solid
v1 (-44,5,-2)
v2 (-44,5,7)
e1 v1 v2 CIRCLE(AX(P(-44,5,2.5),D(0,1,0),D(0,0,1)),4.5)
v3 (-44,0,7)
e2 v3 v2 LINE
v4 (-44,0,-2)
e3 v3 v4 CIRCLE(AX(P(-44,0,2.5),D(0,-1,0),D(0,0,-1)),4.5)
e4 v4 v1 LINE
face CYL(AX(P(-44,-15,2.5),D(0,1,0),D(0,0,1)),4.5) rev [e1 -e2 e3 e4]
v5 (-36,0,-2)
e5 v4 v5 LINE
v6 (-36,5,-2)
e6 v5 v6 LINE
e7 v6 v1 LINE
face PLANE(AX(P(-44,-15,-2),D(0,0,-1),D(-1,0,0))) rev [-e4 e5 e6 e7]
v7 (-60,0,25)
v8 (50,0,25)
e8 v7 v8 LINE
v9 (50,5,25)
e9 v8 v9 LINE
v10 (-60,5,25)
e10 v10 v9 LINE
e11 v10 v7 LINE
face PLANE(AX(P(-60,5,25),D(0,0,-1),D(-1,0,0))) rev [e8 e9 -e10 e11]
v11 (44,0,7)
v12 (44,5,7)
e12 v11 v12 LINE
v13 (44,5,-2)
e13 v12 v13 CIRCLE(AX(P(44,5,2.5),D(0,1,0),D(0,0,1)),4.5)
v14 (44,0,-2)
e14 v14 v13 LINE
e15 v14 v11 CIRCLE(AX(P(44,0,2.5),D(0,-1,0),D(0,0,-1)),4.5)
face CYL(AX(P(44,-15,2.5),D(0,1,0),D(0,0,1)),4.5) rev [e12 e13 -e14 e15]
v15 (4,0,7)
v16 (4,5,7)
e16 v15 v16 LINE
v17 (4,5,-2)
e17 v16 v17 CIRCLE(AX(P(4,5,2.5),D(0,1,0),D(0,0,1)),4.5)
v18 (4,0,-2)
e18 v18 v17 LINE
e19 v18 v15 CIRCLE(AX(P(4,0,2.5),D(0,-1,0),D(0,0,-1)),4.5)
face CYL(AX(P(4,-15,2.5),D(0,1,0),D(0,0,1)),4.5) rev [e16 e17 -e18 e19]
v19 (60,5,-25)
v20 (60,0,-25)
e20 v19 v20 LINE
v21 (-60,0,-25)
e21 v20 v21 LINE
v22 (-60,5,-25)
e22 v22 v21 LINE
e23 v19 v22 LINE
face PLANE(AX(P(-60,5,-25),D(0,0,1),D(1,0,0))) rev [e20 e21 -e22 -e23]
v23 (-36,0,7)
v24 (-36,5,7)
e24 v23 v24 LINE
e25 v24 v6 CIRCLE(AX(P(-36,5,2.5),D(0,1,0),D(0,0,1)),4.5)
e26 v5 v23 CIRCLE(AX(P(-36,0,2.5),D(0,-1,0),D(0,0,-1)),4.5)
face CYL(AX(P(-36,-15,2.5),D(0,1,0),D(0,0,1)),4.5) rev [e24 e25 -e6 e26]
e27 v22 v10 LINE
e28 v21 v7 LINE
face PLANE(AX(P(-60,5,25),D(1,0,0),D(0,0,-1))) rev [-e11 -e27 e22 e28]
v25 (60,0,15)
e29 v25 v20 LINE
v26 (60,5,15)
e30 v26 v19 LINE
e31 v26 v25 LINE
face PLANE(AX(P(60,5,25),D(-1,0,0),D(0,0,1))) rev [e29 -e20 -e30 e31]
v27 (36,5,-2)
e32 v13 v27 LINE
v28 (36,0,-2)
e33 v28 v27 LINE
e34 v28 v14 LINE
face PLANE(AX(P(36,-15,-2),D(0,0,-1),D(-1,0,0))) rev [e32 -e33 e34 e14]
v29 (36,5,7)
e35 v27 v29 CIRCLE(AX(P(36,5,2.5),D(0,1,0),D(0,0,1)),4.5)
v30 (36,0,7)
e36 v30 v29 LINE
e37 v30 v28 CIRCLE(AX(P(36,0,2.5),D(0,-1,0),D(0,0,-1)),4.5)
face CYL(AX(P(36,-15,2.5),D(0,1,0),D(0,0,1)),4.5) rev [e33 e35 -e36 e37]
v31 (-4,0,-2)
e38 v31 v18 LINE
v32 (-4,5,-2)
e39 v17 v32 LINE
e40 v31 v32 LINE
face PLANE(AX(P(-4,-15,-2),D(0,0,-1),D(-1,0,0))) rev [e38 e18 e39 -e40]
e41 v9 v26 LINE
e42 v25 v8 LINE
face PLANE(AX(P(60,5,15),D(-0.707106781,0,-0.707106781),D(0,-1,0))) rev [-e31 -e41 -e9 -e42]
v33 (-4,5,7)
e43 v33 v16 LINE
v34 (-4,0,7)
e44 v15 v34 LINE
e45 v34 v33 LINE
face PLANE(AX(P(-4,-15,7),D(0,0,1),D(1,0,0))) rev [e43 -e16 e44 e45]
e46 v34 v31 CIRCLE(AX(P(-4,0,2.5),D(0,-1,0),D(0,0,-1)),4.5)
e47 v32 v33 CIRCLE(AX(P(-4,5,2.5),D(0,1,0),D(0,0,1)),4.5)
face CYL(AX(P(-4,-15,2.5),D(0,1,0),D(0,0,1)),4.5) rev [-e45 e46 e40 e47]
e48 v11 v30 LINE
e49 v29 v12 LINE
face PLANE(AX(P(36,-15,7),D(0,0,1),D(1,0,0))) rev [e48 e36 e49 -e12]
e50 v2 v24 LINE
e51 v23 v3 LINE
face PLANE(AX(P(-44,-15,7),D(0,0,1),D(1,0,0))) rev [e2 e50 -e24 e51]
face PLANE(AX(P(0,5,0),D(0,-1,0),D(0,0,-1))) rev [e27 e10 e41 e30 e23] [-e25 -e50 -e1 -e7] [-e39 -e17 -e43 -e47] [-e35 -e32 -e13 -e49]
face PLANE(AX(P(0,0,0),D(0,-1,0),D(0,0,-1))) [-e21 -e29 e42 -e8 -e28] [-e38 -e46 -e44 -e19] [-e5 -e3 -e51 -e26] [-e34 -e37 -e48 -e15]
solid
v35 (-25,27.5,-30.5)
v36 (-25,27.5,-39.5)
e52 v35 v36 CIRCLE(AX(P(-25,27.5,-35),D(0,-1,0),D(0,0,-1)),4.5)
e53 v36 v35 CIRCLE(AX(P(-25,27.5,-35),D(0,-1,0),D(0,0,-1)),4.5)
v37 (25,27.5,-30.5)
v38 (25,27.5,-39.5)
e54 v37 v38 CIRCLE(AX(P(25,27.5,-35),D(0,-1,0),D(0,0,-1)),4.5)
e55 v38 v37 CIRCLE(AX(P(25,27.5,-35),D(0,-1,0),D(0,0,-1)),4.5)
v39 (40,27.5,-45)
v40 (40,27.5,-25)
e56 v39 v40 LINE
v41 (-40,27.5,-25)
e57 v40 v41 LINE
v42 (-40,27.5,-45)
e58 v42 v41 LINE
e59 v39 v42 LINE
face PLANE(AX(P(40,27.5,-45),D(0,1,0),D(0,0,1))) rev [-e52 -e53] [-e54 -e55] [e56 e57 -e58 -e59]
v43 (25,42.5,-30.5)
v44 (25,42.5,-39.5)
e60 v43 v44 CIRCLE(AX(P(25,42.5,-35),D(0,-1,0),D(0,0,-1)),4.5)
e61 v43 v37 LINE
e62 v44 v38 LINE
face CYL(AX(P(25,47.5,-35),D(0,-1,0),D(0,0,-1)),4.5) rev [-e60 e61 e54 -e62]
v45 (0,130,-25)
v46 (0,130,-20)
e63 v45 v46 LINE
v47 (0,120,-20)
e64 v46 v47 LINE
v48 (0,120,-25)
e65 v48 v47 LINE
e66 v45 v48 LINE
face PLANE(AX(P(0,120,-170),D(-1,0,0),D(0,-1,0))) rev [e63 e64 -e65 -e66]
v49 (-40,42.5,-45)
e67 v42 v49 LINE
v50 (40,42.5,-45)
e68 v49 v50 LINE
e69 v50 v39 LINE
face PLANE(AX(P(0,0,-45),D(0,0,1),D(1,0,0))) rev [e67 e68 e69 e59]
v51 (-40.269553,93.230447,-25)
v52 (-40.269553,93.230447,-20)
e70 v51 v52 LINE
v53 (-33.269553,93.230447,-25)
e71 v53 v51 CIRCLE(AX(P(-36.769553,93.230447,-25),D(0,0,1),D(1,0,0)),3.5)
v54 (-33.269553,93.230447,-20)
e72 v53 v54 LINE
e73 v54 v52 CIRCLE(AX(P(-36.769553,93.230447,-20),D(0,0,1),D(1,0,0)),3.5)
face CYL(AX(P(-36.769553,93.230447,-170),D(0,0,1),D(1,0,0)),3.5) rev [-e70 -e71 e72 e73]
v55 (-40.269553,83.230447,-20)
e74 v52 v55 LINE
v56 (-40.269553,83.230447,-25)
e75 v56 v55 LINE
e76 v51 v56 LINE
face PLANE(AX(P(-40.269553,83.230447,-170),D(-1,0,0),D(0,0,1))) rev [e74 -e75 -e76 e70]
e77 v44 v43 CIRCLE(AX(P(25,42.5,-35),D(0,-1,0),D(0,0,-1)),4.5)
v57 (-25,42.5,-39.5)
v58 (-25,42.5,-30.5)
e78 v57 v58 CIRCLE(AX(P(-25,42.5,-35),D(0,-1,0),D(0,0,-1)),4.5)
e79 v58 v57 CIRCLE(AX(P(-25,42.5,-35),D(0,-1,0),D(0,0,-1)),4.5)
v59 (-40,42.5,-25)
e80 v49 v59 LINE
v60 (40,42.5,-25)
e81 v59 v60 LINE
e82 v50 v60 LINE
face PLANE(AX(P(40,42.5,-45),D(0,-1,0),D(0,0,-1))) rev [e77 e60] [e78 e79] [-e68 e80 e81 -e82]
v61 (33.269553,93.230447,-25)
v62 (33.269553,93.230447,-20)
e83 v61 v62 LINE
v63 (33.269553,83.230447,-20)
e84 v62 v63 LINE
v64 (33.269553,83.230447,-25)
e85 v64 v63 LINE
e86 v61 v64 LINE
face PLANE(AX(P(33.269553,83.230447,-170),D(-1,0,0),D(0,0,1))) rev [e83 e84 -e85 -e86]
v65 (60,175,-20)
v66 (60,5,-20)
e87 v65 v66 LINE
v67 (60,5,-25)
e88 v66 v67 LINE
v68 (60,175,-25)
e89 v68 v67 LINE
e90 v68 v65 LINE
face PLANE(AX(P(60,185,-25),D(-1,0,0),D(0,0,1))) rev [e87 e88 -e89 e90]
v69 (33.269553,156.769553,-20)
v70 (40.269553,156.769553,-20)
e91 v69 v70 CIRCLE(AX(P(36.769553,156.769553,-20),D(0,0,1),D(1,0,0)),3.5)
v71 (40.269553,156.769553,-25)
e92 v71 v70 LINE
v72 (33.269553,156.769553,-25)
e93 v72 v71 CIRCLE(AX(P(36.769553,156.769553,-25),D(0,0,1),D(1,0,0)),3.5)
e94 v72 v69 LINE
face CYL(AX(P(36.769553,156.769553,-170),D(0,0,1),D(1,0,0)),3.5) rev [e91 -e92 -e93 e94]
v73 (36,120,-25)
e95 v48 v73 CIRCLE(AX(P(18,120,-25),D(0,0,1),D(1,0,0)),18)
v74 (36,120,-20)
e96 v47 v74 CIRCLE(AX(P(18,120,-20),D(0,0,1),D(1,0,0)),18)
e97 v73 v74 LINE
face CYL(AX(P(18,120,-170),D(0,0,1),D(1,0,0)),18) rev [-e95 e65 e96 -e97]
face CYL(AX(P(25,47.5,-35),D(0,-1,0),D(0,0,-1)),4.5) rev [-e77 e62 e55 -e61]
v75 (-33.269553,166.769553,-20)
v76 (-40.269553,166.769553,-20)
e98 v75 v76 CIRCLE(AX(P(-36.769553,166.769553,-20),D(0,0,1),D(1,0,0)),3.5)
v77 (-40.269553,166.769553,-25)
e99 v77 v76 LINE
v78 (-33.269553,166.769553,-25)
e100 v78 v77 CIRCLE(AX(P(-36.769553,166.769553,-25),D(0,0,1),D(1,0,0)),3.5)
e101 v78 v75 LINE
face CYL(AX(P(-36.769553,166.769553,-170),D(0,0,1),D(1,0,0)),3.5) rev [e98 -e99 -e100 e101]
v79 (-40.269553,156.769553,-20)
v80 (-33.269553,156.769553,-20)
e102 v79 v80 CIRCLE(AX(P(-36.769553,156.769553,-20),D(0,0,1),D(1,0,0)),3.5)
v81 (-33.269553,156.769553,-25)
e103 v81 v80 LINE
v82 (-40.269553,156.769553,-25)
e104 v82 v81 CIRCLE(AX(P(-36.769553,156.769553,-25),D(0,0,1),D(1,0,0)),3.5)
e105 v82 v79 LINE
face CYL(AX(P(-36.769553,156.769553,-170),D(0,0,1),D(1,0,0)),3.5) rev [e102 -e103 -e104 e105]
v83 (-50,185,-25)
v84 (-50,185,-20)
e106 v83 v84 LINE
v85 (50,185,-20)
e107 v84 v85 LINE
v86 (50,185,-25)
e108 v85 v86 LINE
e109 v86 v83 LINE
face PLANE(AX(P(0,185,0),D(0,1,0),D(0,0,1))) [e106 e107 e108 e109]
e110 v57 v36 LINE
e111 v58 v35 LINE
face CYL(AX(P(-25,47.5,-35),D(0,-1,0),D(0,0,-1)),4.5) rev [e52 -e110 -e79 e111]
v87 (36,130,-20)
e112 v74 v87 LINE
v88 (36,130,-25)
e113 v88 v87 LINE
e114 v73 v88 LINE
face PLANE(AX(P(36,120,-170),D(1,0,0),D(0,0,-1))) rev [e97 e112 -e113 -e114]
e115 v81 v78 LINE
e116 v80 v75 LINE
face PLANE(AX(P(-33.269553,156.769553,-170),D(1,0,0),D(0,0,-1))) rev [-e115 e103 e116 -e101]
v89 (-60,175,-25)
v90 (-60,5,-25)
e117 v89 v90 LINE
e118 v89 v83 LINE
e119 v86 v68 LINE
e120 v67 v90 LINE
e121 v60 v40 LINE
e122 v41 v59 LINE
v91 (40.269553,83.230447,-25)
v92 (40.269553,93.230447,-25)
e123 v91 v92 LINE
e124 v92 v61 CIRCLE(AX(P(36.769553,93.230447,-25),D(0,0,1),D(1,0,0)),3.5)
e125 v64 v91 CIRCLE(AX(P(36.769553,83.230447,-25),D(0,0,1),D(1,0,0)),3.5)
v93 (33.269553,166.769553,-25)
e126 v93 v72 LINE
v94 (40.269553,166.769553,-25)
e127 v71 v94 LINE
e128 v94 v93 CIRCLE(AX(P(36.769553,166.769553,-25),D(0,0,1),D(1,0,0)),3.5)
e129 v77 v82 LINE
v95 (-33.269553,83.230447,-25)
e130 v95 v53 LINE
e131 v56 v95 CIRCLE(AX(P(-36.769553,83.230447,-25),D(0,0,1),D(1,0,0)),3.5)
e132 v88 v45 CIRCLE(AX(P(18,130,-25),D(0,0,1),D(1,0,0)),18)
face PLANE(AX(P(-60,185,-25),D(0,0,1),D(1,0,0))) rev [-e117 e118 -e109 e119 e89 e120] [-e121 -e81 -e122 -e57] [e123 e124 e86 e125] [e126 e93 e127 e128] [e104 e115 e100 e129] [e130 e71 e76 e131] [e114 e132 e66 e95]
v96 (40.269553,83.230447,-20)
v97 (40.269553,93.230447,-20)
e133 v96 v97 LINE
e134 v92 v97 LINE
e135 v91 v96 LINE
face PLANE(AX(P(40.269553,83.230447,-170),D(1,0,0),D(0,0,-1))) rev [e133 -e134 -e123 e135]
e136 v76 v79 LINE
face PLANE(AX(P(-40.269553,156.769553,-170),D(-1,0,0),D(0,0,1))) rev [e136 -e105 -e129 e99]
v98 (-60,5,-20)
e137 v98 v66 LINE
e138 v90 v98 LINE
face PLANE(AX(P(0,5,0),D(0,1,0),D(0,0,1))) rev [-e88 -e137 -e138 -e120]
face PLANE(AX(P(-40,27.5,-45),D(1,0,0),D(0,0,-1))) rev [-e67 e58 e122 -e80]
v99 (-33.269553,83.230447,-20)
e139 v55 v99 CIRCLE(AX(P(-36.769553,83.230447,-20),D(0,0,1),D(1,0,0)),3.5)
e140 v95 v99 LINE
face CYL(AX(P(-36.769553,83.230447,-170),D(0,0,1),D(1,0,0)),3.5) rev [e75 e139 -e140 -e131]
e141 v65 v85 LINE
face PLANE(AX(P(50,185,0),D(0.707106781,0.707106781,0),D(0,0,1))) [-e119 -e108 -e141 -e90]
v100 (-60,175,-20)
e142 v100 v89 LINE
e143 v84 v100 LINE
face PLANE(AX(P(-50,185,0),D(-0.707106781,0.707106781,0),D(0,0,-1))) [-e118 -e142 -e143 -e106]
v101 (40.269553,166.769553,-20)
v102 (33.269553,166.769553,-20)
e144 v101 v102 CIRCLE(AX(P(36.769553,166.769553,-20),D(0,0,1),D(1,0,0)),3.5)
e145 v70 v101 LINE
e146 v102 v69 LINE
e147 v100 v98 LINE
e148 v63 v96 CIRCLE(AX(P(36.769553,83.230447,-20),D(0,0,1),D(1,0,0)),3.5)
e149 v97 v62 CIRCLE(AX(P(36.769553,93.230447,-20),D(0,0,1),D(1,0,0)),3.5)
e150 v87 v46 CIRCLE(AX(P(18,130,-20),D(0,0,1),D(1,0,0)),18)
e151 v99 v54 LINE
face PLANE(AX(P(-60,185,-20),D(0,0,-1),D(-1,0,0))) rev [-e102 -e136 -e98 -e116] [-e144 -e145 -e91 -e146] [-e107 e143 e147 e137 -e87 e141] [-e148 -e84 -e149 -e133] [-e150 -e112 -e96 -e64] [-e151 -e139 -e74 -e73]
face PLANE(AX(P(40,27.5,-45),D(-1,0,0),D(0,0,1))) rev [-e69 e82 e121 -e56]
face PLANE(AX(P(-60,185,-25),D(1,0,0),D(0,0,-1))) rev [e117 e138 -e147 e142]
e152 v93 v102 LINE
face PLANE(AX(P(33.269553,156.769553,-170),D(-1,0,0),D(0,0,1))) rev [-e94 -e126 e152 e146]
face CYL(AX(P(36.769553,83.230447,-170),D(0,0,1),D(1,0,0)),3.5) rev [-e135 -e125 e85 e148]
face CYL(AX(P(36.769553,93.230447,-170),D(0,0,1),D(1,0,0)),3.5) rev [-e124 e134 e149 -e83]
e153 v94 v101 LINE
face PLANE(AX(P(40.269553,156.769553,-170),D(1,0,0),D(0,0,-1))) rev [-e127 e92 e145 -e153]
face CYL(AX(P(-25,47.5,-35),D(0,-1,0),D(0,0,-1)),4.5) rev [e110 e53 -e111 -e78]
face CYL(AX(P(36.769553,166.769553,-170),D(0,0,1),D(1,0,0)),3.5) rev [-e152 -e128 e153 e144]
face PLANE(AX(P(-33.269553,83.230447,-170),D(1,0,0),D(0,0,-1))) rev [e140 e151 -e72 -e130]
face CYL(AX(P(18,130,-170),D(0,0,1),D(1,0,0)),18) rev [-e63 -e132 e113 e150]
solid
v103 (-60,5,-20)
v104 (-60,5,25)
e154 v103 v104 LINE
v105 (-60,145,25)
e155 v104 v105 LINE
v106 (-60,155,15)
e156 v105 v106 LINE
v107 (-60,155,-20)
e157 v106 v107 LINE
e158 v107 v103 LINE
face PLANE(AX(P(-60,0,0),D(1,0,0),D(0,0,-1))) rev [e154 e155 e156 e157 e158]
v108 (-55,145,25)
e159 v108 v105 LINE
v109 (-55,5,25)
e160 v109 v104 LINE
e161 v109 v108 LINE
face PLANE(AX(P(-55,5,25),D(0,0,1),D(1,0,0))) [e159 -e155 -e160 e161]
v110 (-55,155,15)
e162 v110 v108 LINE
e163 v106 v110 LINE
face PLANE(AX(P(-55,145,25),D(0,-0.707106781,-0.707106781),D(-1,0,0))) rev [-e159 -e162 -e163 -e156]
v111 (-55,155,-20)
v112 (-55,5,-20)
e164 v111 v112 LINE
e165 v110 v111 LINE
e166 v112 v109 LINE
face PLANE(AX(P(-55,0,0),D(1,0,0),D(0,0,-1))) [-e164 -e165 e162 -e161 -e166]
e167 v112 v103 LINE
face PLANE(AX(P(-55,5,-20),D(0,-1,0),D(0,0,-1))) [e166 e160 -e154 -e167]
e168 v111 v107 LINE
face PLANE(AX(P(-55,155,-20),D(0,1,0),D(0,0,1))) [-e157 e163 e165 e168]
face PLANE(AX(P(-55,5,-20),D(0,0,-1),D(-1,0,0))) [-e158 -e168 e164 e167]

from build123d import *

# Parameters (mm, degrees)
SKETCH_1_W          = 120
SKETCH_1_H          = 50
EXTRUDE_1_DEPTH     = 5
SKETCH_2_W          = 120
SKETCH_2_H          = 5
EXTRUDE_2_DEPTH     = 180
CUT_EXTRUDE_1_DEPTH = 150
CHAMFER_1_SIZE      = 10
SKETCH_5_W          = 45
SKETCH_5_H          = 150
EXTRUDE_3_DEPTH     = 5
CHAMFER_2_SIZE      = 10
SKETCH_6_W          = 80
SKETCH_6_H          = 15
EXTRUDE_4_DEPTH     = 20
CUT_EXTRUDE_2_DEPTH = 20
CHAMFER_3_SIZE      = 10
SKETCH_10_R         = 4.5
CUT_EXTRUDE_3_DEPTH = 20


with BuildPart() as part:
    # 草图1 → 凸台-拉伸1 (new body)
    with BuildSketch(Plane(origin=(0, 0, 0), x_dir=(1, 0, 0), z_dir=(0, 1, 0))):
        Rectangle(SKETCH_1_W, SKETCH_1_H)
    extrude(amount=EXTRUDE_1_DEPTH)

    # 草图9 → 切除-拉伸2 (cut)
    with BuildSketch(Plane(origin=(0, 5, 0), x_dir=(1, 0, 0), z_dir=(0, 1, 0))):
        with BuildLine():
            Line((-44, 2), (-36, 2))
            ThreePointArc((-36, 2), (-31.5, -2.5), (-36, -7))
            Line((-36, -7), (-44, -7))
            ThreePointArc((-44, -7), (-48.5, -2.5), (-44, 2))
        make_face()
        with BuildLine():
            Line((-4, 2), (4, 2))
            ThreePointArc((4, 2), (8.5, -2.5), (4, -7))
            Line((4, -7), (-4, -7))
            ThreePointArc((-4, -7), (-8.5, -2.5), (-4, 2))
        make_face()
        with BuildLine():
            Line((36, 2), (44, 2))
            ThreePointArc((44, 2), (48.5, -2.5), (44, -7))
            Line((44, -7), (36, -7))
            ThreePointArc((36, -7), (31.5, -2.5), (36, 2))
        make_face()
    extrude(amount=-CUT_EXTRUDE_2_DEPTH, mode=Mode.SUBTRACT)

    # 倒角3
    chamfer_3_edges = [part.edges().sort_by_distance(p)[0] for p in [
        (60, 2.5, 25),
    ]]
    chamfer(chamfer_3_edges, length=CHAMFER_3_SIZE)


with BuildPart() as body_2:
    # 草图2 → 凸台-拉伸2 (new body)
    with BuildSketch(Plane(origin=(0, 5, 0), x_dir=(1, 0, 0), z_dir=(0, 1, 0))):
        with Locations((0, 22.5)):
            Rectangle(SKETCH_2_W, SKETCH_2_H)
    extrude(amount=EXTRUDE_2_DEPTH)

    # 草图3 → 切除-拉伸1 (cut)
    with BuildSketch(Plane.XY.offset(-20)):
        with BuildLine():
            Line((-40.269552622, 83.230447378), (-40.269552622, 93.230447378))
            ThreePointArc((-40.269552622, 93.230447378), (-36.769552622, 96.730447378), (-33.269552622, 93.230447378))
            Line((-33.269552622, 93.230447378), (-33.269552622, 83.230447378))
            ThreePointArc((-33.269552622, 83.230447378), (-36.769552622, 79.730447378), (-40.269552622, 83.230447378))
        make_face()
        with BuildLine():
            Line((33.269552622, 83.230447378), (33.269552622, 93.230447378))
            ThreePointArc((33.269552622, 93.230447378), (36.769552622, 96.730447378), (40.269552622, 93.230447378))
            Line((40.269552622, 93.230447378), (40.269552622, 83.230447378))
            ThreePointArc((40.269552622, 83.230447378), (36.769552622, 79.730447378), (33.269552622, 83.230447378))
        make_face()
        with BuildLine():
            Line((33.269552622, 156.769552622), (33.269552622, 166.769552622))
            ThreePointArc((33.269552622, 166.769552622), (36.769552622, 170.269552622), (40.269552622, 166.769552622))
            Line((40.269552622, 166.769552622), (40.269552622, 156.769552622))
            ThreePointArc((40.269552622, 156.769552622), (36.769552622, 153.269552622), (33.269552622, 156.769552622))
        make_face()
        with BuildLine():
            Line((-40.269552622, 156.769552622), (-40.269552622, 166.769552622))
            ThreePointArc((-40.269552622, 166.769552622), (-36.769552622, 170.269552622), (-33.269552622, 166.769552622))
            Line((-33.269552622, 166.769552622), (-33.269552622, 156.769552622))
            ThreePointArc((-33.269552622, 156.769552622), (-36.769552622, 153.269552622), (-40.269552622, 156.769552622))
        make_face()
        with BuildLine():
            Line((0, 120), (0, 130))
            ThreePointArc((0, 130), (18, 148), (36, 130))
            Line((36, 130), (36, 120))
            ThreePointArc((36, 120), (18, 102), (0, 120))
        make_face()
    extrude(amount=-CUT_EXTRUDE_1_DEPTH, mode=Mode.SUBTRACT)

    # 倒角1
    chamfer_1_edges = [body_2.edges().sort_by_distance(p)[0] for p in [
        (60, 185, -22.5),
        (-60, 185, -22.5),
    ]]
    chamfer(chamfer_1_edges, length=CHAMFER_1_SIZE)

    # 草图6 → 凸台-拉伸4 (add)
    with BuildSketch(Plane(origin=(0, 0, -25), x_dir=(-1, 0, 0), z_dir=(0, 0, -1))):
        with Locations((0, 35)):
            Rectangle(SKETCH_6_W, SKETCH_6_H)
    extrude(amount=EXTRUDE_4_DEPTH)

    # 草图10 → 切除-拉伸3 (cut)
    with BuildSketch(Plane.XZ.offset(-27.5)):
        with Locations(Location((-25, -35, 0), (0, 0, 270))):
            Circle(SKETCH_10_R)
        with Locations(Location((25, -35, 0), (0, 0, 270))):
            Circle(SKETCH_10_R)
    extrude(amount=-CUT_EXTRUDE_3_DEPTH, mode=Mode.SUBTRACT)


with BuildPart() as body_3:
    # 草图5 → 凸台-拉伸3 (new body)
    with BuildSketch(Plane.ZY.offset(60)):
        with Locations((2.5, 80)):
            Rectangle(SKETCH_5_W, SKETCH_5_H)
    extrude(amount=-EXTRUDE_3_DEPTH)

    # 倒角2
    chamfer_2_edges = [body_3.edges().sort_by_distance(p)[0] for p in [
        (-57.5, 155, 25),
    ]]
    chamfer(chamfer_2_edges, length=CHAMFER_2_SIZE)


solid = Compound([part.part, body_2.part, body_3.part])
